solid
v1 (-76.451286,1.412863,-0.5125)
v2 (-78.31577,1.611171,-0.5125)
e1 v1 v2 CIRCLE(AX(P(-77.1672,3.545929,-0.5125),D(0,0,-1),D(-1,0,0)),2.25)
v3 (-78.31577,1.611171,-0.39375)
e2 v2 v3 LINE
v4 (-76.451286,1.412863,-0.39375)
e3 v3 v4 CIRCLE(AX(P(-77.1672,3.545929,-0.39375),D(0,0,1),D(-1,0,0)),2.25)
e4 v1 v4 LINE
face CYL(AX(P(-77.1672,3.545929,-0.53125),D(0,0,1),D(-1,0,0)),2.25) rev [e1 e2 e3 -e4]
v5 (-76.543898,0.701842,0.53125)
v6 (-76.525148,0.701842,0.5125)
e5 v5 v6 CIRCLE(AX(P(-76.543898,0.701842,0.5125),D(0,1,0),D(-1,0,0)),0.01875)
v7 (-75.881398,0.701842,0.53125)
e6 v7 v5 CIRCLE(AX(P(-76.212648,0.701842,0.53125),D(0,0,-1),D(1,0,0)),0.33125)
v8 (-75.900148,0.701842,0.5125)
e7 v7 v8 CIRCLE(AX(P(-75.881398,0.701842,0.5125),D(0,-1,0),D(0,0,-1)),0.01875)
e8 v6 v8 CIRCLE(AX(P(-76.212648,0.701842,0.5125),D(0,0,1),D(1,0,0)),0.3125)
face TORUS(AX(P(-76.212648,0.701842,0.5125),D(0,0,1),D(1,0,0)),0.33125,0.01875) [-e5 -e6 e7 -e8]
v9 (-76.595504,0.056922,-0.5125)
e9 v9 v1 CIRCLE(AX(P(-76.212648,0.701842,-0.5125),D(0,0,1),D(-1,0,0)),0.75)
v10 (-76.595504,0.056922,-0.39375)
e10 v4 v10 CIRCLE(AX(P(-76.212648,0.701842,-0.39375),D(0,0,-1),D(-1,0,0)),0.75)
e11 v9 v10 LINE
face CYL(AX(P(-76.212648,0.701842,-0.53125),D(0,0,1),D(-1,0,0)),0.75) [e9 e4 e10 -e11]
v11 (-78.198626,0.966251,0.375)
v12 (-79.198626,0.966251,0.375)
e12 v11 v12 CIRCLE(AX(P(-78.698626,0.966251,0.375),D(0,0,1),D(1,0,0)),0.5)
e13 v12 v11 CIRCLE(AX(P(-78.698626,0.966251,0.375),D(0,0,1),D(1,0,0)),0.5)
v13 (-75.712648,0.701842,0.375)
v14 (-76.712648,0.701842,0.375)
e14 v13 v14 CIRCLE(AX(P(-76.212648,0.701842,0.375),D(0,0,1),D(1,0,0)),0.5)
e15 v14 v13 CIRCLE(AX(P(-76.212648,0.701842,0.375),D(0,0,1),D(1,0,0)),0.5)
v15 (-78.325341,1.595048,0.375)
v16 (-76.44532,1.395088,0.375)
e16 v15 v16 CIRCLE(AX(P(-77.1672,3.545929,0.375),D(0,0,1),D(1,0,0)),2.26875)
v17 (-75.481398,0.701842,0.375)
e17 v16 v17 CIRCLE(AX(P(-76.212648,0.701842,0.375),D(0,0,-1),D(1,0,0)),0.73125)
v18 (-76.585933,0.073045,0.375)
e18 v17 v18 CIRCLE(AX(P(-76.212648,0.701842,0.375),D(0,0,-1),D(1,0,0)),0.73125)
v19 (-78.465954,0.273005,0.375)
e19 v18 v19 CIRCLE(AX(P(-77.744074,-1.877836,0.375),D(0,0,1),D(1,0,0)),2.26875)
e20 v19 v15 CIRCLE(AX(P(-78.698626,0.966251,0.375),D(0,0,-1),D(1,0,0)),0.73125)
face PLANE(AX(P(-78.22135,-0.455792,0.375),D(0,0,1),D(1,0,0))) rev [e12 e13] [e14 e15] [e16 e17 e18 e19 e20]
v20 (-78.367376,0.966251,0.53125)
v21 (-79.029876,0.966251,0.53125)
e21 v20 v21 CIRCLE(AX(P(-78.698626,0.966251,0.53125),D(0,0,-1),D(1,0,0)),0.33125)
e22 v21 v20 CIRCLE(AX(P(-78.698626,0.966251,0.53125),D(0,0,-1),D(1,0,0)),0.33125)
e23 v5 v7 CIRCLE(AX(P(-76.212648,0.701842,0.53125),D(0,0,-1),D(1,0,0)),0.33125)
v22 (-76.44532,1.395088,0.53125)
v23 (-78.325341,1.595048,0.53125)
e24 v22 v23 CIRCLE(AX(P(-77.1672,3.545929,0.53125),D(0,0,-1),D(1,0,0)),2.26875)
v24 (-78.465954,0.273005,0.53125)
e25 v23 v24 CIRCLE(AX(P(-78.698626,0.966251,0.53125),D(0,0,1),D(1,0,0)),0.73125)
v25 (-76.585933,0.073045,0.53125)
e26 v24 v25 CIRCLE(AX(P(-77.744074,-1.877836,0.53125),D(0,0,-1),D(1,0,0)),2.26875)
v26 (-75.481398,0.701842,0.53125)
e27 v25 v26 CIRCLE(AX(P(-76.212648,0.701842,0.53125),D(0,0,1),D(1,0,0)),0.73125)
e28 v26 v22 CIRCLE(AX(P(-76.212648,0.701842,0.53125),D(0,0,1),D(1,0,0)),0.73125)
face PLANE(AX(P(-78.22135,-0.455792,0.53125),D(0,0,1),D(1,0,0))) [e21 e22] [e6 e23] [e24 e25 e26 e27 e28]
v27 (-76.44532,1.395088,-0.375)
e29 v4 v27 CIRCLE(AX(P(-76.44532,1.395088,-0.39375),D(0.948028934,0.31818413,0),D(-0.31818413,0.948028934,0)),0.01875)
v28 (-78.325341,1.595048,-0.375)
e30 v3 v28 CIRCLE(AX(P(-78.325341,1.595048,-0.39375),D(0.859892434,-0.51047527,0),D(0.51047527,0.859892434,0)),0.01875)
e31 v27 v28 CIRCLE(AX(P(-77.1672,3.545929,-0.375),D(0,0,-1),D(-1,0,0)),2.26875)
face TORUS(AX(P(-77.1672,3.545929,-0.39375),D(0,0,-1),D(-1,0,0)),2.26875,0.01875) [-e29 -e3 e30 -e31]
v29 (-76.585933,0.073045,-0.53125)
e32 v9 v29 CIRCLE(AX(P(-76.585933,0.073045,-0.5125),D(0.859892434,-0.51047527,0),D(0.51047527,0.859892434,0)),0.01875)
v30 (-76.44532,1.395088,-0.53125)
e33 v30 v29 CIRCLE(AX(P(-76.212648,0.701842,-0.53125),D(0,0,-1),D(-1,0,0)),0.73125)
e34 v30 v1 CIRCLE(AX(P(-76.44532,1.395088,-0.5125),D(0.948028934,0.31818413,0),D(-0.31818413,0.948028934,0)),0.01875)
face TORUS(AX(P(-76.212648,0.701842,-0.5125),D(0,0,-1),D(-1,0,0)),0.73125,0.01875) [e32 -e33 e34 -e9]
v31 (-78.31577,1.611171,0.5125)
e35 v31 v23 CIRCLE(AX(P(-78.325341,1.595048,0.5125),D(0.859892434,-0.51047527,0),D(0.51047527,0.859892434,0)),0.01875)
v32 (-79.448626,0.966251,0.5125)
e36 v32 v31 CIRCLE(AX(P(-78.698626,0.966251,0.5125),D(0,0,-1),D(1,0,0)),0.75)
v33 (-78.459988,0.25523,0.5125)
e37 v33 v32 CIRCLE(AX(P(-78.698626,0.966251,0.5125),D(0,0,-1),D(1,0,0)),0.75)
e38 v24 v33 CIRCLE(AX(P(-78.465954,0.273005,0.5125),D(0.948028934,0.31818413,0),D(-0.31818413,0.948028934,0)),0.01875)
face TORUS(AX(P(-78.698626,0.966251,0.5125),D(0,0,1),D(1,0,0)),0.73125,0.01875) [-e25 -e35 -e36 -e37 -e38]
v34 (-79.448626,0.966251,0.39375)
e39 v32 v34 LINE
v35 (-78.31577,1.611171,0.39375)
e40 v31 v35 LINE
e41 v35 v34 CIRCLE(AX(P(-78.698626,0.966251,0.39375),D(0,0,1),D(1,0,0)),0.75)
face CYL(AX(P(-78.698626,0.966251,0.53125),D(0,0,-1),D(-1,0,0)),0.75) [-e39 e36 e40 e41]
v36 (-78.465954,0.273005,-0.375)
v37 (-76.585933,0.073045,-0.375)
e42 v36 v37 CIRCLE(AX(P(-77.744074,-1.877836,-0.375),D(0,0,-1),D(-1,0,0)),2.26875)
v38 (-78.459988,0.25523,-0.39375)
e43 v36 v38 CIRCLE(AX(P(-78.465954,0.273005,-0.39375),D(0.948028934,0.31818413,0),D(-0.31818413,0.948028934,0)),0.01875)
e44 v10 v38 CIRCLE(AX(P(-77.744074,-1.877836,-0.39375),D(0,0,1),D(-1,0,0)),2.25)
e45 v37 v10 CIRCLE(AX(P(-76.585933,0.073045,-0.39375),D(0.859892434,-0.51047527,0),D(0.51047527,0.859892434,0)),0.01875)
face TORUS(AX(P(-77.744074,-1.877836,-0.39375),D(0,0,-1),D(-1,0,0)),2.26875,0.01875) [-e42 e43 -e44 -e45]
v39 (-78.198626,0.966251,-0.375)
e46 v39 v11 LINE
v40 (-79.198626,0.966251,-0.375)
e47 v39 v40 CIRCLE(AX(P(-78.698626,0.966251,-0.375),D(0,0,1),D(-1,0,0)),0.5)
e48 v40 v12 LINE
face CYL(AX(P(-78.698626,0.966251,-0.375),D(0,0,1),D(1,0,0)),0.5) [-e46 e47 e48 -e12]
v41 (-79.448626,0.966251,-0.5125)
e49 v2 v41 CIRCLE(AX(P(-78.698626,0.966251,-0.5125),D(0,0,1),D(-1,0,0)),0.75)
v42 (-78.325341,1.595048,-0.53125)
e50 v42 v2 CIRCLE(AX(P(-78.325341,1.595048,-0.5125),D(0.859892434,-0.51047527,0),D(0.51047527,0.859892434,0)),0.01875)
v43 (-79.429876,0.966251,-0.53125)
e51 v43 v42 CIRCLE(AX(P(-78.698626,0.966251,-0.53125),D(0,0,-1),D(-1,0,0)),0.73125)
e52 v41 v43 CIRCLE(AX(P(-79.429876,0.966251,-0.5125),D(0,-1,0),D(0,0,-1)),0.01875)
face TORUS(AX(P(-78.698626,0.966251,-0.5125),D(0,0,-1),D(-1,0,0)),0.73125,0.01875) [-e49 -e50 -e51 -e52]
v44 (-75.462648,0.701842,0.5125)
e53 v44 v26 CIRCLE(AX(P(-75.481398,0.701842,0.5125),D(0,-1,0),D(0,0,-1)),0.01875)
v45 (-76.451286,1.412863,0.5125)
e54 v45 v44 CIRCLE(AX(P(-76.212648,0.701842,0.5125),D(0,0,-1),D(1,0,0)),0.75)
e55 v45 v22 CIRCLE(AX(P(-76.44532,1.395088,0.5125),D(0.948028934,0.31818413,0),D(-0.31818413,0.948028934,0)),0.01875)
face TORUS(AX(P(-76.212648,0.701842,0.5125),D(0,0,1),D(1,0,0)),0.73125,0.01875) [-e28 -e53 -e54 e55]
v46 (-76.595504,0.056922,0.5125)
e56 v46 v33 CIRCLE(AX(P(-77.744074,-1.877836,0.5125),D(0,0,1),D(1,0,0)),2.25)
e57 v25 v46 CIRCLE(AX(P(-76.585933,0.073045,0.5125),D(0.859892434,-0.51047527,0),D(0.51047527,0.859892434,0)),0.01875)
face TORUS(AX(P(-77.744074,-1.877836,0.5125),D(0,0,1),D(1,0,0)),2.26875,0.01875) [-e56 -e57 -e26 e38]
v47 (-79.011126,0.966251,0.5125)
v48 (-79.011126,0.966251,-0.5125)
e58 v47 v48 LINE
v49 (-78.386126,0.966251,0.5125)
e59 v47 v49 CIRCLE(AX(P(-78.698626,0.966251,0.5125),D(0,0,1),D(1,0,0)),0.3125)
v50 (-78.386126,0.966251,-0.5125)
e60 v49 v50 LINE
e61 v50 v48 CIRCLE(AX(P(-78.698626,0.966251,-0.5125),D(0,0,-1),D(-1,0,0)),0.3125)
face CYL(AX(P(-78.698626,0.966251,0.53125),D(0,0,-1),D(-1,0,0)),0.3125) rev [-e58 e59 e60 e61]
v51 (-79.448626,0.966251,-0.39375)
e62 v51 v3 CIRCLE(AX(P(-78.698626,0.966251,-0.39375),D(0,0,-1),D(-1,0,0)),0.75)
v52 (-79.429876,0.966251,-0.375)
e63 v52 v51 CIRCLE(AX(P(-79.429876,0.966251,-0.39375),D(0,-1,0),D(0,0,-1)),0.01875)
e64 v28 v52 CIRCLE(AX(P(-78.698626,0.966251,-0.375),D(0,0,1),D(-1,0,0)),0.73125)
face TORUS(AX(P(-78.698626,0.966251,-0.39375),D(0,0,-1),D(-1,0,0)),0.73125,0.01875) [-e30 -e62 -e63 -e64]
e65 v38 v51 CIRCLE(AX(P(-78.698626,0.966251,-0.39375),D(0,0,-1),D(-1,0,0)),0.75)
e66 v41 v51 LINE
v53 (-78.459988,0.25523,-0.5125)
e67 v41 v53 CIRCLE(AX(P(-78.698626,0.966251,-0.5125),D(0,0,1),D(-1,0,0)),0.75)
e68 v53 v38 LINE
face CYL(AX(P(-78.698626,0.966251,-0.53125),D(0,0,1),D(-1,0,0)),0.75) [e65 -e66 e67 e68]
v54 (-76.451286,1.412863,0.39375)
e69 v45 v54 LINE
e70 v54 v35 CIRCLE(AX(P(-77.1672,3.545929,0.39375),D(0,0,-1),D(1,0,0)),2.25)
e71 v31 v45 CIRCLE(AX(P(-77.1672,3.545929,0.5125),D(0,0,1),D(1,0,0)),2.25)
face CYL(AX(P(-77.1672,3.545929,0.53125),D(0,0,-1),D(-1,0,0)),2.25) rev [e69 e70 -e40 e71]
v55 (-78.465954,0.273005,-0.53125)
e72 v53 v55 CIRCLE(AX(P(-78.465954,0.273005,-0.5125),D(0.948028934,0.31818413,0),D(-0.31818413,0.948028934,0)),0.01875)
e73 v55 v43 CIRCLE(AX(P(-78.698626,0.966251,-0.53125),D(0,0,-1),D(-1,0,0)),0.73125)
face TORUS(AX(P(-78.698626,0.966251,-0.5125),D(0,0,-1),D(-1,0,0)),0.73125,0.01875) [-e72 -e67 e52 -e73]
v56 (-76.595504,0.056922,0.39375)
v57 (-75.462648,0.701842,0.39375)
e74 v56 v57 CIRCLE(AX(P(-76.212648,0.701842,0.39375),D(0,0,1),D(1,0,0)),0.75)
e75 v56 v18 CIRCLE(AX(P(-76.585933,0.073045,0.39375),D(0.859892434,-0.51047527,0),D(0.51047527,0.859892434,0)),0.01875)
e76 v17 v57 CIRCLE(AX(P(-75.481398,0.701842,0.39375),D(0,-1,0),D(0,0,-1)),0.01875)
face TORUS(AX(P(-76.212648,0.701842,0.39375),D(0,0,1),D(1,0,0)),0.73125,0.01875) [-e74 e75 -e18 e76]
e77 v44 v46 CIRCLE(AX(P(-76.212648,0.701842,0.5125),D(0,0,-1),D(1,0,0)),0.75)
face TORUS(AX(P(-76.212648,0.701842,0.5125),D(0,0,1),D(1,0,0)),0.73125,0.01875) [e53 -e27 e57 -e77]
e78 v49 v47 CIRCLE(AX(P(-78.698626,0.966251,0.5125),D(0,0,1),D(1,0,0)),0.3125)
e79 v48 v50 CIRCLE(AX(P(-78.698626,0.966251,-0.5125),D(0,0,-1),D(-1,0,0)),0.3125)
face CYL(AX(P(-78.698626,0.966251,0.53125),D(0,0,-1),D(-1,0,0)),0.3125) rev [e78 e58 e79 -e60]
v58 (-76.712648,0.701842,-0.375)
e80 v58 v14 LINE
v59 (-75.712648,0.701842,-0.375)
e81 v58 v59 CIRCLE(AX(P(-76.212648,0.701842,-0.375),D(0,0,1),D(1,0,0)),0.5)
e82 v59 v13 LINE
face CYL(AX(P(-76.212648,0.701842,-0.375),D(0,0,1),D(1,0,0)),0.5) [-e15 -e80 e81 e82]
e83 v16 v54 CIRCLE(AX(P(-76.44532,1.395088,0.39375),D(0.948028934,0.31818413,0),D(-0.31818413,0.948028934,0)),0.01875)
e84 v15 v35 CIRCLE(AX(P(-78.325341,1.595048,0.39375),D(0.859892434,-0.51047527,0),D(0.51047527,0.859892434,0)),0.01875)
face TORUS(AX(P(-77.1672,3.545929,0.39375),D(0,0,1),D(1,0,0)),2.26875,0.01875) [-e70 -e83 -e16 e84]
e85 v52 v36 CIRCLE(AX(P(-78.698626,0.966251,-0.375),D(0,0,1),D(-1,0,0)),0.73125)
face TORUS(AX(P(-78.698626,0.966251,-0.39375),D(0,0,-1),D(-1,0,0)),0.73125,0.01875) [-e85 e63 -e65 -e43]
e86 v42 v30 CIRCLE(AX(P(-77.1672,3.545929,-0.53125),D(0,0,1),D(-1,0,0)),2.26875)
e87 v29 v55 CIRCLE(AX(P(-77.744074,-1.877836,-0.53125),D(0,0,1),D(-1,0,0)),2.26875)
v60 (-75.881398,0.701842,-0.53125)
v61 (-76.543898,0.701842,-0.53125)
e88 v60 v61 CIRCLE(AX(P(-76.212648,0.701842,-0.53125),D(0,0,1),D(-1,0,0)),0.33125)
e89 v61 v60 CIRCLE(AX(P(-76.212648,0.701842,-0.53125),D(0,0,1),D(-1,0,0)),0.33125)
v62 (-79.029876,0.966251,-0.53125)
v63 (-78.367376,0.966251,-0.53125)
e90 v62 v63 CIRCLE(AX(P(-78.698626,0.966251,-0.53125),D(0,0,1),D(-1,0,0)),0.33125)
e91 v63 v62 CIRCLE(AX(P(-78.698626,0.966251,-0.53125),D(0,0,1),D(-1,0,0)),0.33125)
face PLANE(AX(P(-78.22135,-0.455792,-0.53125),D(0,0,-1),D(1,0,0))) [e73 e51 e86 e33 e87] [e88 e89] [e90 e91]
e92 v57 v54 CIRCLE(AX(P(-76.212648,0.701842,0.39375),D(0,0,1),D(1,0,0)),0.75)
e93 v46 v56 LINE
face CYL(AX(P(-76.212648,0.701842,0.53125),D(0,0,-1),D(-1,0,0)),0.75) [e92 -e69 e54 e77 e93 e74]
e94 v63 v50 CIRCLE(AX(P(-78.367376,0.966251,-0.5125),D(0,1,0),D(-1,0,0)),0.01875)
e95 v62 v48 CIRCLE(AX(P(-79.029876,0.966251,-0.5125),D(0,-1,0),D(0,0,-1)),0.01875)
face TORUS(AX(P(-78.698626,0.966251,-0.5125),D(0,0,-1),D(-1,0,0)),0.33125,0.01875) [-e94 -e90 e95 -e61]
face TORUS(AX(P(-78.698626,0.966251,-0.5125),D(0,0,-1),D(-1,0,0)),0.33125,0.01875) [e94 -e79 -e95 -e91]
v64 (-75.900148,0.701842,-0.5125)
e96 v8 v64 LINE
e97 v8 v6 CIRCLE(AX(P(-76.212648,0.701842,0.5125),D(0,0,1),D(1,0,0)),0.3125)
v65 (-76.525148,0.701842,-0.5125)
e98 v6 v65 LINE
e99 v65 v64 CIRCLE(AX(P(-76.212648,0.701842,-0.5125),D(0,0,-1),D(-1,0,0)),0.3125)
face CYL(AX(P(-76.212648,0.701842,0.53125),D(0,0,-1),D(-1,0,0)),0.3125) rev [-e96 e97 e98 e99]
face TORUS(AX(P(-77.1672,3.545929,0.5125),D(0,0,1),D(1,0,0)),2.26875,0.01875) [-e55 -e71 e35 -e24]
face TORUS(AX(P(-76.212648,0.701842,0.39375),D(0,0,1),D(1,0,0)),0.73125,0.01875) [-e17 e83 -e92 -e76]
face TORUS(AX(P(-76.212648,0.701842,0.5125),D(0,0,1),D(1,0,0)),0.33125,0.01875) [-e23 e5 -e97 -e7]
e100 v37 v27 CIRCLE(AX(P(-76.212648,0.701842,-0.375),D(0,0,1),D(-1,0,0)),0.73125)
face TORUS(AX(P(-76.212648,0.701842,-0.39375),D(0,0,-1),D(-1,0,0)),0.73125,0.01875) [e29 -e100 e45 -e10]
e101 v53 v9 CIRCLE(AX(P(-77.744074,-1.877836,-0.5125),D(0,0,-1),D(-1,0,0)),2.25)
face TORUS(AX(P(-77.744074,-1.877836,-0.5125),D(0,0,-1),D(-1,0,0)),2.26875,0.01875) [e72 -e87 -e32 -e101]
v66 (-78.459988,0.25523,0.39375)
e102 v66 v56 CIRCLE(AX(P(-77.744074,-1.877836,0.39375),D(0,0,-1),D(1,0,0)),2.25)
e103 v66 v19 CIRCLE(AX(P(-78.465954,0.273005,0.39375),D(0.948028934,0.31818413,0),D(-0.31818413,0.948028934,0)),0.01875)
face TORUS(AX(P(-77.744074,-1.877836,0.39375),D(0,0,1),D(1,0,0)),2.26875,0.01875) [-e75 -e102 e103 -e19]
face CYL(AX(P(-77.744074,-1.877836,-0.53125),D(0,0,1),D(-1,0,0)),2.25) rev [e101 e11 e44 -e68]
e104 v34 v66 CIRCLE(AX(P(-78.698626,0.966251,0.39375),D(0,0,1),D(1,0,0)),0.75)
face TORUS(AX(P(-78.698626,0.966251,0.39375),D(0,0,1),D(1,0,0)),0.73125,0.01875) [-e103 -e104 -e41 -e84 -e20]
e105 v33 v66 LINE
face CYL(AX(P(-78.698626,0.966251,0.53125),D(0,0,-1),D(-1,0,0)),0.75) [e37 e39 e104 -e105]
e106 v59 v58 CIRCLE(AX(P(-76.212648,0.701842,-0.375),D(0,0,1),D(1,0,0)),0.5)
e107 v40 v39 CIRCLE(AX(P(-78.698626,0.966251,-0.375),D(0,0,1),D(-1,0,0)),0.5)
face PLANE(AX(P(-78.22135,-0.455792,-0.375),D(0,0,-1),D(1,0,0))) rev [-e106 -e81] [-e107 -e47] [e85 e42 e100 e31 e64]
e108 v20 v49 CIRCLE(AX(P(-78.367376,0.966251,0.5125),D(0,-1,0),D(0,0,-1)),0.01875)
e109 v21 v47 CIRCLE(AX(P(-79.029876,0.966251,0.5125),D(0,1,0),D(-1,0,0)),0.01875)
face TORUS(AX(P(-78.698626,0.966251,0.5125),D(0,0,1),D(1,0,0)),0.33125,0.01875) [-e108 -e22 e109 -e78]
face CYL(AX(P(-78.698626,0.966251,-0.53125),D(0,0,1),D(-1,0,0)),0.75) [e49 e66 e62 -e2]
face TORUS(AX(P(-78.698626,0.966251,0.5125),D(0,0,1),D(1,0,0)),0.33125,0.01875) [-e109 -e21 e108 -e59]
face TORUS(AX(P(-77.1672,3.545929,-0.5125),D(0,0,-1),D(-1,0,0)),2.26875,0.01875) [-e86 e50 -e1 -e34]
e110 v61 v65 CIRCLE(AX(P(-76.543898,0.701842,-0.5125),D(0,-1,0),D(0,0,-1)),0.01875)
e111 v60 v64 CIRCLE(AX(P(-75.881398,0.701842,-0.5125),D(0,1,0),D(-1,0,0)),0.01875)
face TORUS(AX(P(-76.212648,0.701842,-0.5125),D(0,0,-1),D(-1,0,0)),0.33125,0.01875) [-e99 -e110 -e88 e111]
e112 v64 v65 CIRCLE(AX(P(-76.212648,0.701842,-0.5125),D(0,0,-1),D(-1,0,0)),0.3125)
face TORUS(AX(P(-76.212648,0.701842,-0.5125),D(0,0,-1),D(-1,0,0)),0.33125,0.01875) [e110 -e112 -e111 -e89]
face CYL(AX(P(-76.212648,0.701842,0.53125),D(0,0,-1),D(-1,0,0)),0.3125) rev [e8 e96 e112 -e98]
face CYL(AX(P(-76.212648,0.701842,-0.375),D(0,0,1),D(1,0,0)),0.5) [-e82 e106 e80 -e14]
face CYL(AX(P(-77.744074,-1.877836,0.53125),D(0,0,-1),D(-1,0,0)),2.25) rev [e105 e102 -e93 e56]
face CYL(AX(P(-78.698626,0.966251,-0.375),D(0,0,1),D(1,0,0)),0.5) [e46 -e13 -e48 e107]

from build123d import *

# Parameters (mm, degrees)
BOSS_EXTRUDE1_DEPTH        = 3
BOSS_EXTRUDE1_DEPTH_BACK   = 3
SKETCH3_R                  = 4
SKETCH3_R_2                = 2.5
BOSS_EXTRUDE1_2_DEPTH      = 3
BOSS_EXTRUDE1_2_DEPTH_BACK = 3
SKETCH5_R                  = 2.5
BOSS_EXTRUDE2_DEPTH        = 1.25
FILLET1_R                  = 0.15
SCALE1_SCALE               = 0.5
SCALE2_SCALE               = 0.5
SCALE3_SCALE               = 0.5


with BuildPart() as part:
    # Sketch3 → Boss-Extrude1 (new, two sides: drawn at the far end of the back side and taken through both)
    with BuildSketch(Plane.XY.offset(-BOSS_EXTRUDE1_DEPTH_BACK)):
        with Locations((-87.399549733, 1.891684495)):
            Circle(SKETCH3_R)
        with Locations((-87.399549733, 1.891684495)):
            Circle(SKETCH3_R_2, mode=Mode.SUBTRACT)
    extrude(amount=BOSS_EXTRUDE1_DEPTH + BOSS_EXTRUDE1_DEPTH_BACK)


with BuildPart() as body_2:
    # Sketch3 → Boss-Extrude1 2 (new, two sides: drawn at the far end of the back side and taken through both)
    with BuildSketch(Plane.XY.offset(-BOSS_EXTRUDE1_2_DEPTH_BACK)):
        with Locations((-67.511724124, -0.223591499)):
            Circle(SKETCH3_R)
        with Locations((-67.511724124, -0.223591499)):
            Circle(SKETCH3_R_2, mode=Mode.SUBTRACT)
    extrude(amount=BOSS_EXTRUDE1_2_DEPTH + BOSS_EXTRUDE1_2_DEPTH_BACK)


with BuildPart() as body_3:
    # Sketch5 → Boss-Extrude2 (new body)
    with BuildSketch(Plane.XY.offset(3)):
        with BuildLine():
            ThreePointArc((-70.574575747, -5.382946104), (-61.545376441, -0.858174297), (-69.420828904, 5.464582104))
            ThreePointArc((-69.420828904, 5.464582104), (-77.051891637, 4.630059865), (-84.336698111, 7.0510391))
            ThreePointArc((-84.336698111, 7.0510391), (-93.365897416, 2.526267293), (-85.490444954, -3.796489108))
            ThreePointArc((-85.490444954, -3.796489108), (-77.85938222, -2.961966869), (-70.574575747, -5.382946104))
        make_face()
        with Locations((-67.511724124, -0.223591499)):
            Circle(SKETCH5_R, mode=Mode.SUBTRACT)
        with Locations((-87.399549733, 1.891684495)):
            Circle(SKETCH5_R, mode=Mode.SUBTRACT)
    extrude(amount=BOSS_EXTRUDE2_DEPTH)


with BuildPart() as body_4:
    # Mirror1: mirrored copy
    add(body_3.part.mirror(Plane.XY))


with BuildPart() as body_3_1:
    add(body_3.part)

    # Combine1: union part, body 4, body 2
    add(part.part)
    add(body_4.part)
    add(body_2.part)

    # Fillet1
    fillet1_edges = [body_3_1.edges().sort_by_distance(p)[0] for p in [
        (-70.011724124, -0.223591499, 4.25),
        (-77.051891637, 4.630059865, 4.25),
        (-89.899549733, 1.891684495, 4.25),
        (-93.365897416, 2.526267293, 4.25),
        (-70.011724124, -0.223591499, -4.25),
        (-89.899549733, 1.891684495, -4.25),
        (-77.85938222, -2.961966869, -3),
        (-61.545376441, -0.858174297, -3),
        (-77.051891637, 4.630059865, -3),
        (-93.365897416, 2.526267293, -3),
        (-77.85938222, -2.961966869, -4.25),
        (-61.545376441, -0.858174297, -4.25),
        (-77.051891637, 4.630059865, -4.25),
        (-93.365897416, 2.526267293, -4.25),
        (-77.85938222, -2.961966869, 4.25),
        (-93.365897416, 2.526267293, 3),
        (-77.051891637, 4.630059865, 3),
        (-61.545376441, -0.858174297, 3),
        (-77.85938222, -2.961966869, 3),
        (-61.545376441, -0.858174297, 4.25),
    ]]
    fillet(fillet1_edges, radius=FILLET1_R)


with BuildPart() as body_3_2:
    # Scale1: scaled about (-77.455636929, 0.834046498, 0)
    add(body_3_1.part.scale(SCALE1_SCALE).moved(Location((-38.727818464, 0.417023249, 0))))


with BuildPart() as body_3_3:
    # Scale2: scaled about (-77.455636929, 0.834046498, 0)
    add(body_3_2.part.scale(SCALE2_SCALE).moved(Location((-38.727818464, 0.417023249, 0))))


with BuildPart() as body_3_4:
    # Scale3: scaled about (-77.455636929, 0.834046498, 0)
    add(body_3_3.part.scale(SCALE3_SCALE).moved(Location((-38.727818464, 0.417023249, 0))))


solid = body_3_4.part
